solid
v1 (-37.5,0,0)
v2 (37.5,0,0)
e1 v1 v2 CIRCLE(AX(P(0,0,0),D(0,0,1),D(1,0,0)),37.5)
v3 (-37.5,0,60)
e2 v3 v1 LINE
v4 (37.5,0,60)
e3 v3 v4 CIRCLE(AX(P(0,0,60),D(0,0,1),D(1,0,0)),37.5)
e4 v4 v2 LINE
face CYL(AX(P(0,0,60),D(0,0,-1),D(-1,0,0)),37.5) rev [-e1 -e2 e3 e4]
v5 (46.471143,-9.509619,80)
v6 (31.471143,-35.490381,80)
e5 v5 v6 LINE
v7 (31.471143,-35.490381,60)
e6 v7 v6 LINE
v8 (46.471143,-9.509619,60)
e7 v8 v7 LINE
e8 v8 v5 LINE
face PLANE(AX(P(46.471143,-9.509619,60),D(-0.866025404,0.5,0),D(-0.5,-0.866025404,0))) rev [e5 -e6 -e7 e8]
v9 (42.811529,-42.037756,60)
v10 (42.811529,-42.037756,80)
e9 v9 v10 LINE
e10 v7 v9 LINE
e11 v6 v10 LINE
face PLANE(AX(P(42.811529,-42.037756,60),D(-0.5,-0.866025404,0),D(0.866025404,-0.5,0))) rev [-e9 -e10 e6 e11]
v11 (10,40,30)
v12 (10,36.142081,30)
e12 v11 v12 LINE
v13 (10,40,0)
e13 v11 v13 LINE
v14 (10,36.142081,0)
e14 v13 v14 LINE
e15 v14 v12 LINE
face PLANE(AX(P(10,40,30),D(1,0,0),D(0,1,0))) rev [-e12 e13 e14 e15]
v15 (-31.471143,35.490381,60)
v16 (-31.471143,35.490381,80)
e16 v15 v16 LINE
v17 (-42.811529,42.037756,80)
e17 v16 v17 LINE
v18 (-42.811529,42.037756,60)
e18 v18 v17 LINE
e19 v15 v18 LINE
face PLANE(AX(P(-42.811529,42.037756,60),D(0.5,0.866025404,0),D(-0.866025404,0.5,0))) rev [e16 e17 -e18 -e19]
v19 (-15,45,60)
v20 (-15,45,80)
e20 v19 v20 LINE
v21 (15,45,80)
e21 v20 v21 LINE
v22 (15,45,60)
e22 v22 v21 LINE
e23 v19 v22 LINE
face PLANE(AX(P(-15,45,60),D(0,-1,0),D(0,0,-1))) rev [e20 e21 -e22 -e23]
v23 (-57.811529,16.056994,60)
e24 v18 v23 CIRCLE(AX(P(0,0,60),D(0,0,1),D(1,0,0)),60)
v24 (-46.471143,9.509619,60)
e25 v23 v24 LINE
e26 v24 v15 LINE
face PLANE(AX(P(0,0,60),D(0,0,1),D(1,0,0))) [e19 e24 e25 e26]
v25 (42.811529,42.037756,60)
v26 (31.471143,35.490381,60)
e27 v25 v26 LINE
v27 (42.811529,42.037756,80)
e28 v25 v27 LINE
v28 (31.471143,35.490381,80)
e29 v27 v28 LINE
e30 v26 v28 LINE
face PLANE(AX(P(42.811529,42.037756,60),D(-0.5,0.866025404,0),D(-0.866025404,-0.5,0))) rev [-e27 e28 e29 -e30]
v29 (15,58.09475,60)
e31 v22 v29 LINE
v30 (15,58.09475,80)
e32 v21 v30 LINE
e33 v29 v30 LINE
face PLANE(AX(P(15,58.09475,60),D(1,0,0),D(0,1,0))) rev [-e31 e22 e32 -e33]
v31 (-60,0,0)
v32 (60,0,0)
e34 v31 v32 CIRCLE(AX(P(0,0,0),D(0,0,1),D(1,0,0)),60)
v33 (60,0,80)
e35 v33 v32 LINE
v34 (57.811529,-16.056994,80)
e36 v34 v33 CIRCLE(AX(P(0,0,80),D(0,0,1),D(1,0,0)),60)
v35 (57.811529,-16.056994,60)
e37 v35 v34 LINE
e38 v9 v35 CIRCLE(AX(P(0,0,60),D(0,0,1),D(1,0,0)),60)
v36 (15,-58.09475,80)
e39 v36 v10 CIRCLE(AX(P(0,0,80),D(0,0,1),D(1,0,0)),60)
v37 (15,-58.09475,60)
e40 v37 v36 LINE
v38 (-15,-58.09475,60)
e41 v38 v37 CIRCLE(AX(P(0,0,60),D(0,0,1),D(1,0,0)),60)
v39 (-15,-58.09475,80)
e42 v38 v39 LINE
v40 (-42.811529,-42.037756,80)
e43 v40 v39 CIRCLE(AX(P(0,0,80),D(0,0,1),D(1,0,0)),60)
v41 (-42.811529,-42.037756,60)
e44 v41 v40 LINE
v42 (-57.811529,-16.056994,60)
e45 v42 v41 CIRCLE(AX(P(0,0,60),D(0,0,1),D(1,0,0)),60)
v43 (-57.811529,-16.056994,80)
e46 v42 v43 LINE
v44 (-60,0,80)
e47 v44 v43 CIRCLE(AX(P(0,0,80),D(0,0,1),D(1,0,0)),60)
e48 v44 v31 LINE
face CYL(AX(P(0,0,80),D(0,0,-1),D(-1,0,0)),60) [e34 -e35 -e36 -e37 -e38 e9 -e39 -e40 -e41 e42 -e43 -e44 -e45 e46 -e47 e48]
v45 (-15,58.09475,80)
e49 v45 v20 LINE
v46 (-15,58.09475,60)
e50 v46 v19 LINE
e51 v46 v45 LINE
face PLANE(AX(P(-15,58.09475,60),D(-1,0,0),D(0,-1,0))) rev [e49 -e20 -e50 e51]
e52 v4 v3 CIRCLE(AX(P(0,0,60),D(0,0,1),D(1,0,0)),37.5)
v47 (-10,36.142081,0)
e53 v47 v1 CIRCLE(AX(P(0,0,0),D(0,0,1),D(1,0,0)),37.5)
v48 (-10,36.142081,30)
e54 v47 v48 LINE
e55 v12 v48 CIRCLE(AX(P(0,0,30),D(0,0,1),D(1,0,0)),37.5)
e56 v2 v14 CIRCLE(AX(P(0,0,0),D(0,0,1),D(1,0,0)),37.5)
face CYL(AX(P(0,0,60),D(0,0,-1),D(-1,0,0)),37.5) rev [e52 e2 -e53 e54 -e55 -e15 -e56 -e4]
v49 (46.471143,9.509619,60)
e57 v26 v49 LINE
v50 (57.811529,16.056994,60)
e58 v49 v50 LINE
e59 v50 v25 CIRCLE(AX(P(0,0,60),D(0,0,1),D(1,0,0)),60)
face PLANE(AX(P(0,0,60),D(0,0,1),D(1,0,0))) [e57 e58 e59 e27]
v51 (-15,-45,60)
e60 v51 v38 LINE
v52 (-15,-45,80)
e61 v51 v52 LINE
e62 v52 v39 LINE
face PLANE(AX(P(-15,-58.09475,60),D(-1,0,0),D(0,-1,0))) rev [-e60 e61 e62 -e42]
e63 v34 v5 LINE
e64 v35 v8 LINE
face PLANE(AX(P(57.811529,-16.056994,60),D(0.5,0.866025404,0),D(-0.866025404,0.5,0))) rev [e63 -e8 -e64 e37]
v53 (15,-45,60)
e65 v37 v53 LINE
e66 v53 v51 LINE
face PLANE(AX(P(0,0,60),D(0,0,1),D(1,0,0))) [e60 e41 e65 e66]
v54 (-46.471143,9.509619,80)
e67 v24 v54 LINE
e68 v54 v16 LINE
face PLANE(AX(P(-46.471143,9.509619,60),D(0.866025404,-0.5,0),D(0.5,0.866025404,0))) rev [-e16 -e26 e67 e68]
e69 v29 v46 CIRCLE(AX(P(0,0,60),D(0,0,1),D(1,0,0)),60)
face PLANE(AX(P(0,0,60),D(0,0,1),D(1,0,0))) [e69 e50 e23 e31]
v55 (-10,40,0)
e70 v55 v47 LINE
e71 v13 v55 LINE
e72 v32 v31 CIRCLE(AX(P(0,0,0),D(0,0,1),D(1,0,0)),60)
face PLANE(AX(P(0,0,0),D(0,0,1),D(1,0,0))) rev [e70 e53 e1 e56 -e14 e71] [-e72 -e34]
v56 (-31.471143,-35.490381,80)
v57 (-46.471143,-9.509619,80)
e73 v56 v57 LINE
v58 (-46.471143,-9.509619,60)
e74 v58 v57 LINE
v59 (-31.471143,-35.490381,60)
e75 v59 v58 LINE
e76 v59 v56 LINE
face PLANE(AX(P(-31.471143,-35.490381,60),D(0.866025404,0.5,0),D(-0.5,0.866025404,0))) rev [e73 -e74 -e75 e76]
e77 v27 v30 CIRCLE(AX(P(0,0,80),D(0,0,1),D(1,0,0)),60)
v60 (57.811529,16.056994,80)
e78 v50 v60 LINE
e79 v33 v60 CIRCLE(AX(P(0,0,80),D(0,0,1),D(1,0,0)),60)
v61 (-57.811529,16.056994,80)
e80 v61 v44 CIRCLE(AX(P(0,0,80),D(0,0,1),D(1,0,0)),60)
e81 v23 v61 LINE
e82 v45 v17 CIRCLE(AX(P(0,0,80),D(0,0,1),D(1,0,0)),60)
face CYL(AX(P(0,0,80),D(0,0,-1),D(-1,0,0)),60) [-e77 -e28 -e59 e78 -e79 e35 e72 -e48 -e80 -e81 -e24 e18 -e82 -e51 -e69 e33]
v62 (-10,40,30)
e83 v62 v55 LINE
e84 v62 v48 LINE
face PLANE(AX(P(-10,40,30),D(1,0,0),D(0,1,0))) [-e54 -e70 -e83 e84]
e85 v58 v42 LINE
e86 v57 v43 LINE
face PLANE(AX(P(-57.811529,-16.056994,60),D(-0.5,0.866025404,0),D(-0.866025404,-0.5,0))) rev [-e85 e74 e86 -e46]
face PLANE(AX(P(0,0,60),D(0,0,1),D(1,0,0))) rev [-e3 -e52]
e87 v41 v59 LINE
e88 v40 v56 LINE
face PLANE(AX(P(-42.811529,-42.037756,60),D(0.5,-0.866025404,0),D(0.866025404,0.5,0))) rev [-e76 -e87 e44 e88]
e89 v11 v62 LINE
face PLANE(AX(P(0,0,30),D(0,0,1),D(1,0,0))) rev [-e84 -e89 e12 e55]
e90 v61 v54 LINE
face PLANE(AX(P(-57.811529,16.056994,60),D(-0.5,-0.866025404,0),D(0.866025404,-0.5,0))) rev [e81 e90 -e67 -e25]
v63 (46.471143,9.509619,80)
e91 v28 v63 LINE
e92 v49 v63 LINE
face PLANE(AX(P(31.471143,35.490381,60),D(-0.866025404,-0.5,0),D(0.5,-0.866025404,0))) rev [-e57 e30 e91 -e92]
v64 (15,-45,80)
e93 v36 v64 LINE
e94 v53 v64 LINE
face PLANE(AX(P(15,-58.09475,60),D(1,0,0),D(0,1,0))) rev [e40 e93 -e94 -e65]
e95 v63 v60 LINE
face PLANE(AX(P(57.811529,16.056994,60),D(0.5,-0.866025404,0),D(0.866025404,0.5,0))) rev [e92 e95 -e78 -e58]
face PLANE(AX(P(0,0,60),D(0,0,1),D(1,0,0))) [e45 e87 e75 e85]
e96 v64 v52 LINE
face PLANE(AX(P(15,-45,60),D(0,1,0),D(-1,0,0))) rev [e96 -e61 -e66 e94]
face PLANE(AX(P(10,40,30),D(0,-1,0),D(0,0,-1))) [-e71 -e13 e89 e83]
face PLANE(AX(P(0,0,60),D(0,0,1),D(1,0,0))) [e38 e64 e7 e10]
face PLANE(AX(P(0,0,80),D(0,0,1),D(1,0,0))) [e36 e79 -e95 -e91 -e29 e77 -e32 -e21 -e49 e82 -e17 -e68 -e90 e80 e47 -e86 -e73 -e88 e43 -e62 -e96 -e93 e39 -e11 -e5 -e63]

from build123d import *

# Parameters (mm, degrees)
SKETCH_2_R          = 60
EXTRUDE_1_DEPTH     = 80
SKETCH_1_R          = 37.5
CUT_EXTRUDE_1_DEPTH = 60
CUT_EXTRUDE_START   = -20
CUT_EXTRUDE_2_DEPTH = 20
SKETCH_4_W          = 20
SKETCH_4_H          = 11.668393693
CUT_EXTRUDE_3_DEPTH = 30


with BuildPart() as part:
    # 草图2 → 凸台-拉伸1 (new body)
    with BuildSketch(Plane.XY):
        Circle(SKETCH_2_R)
    extrude(amount=EXTRUDE_1_DEPTH)

    # 草图1 → 切除-拉伸1 (cut)
    with BuildSketch(Plane.XY):
        Circle(SKETCH_1_R)
    extrude(amount=CUT_EXTRUDE_1_DEPTH, mode=Mode.SUBTRACT)

    # 草图3 → 切除-拉伸2 (cut)
    with BuildSketch(Plane.XY.offset(80).offset(CUT_EXTRUDE_START)):
        with BuildLine():
            Line((57.811529494, 16.05699404), (46.47114317, 9.509618943))
            Line((46.47114317, 9.509618943), (31.47114317, 35.490381057))
            Line((31.47114317, 35.490381057), (42.811529494, 42.037756153))
            ThreePointArc((42.811529494, 42.037756153), (51.961524227, 30), (57.811529494, 16.05699404))
        make_face()
        with BuildLine():
            Line((-15, 58.094750193), (-15, 45))
            Line((-15, 45), (15, 45))
            Line((15, 45), (15, 58.094750193))
            ThreePointArc((15, 58.094750193), (0, 60), (-15, 58.094750193))
        make_face()
        with BuildLine():
            Line((42.811529494, -42.037756153), (31.47114317, -35.490381057))
            Line((31.47114317, -35.490381057), (46.47114317, -9.509618943))
            Line((46.47114317, -9.509618943), (57.811529494, -16.05699404))
            ThreePointArc((57.811529494, -16.05699404), (51.961524227, -30), (42.811529494, -42.037756153))
        make_face()
        with BuildLine():
            Line((-15, -58.094750193), (-15, -45))
            Line((-15, -45), (15, -45))
            Line((15, -45), (15, -58.094750193))
            ThreePointArc((15, -58.094750193), (0, -60), (-15, -58.094750193))
        make_face()
        with BuildLine():
            Line((-57.811529494, -16.05699404), (-46.47114317, -9.509618943))
            Line((-46.47114317, -9.509618943), (-31.47114317, -35.490381057))
            Line((-31.47114317, -35.490381057), (-42.811529494, -42.037756153))
            ThreePointArc((-42.811529494, -42.037756153), (-51.961524227, -30), (-57.811529494, -16.05699404))
        make_face()
        with BuildLine():
            Line((-42.811529494, 42.037756153), (-31.47114317, 35.490381057))
            Line((-31.47114317, 35.490381057), (-46.47114317, 9.509618943))
            Line((-46.47114317, 9.509618943), (-57.811529494, 16.05699404))
            ThreePointArc((-57.811529494, 16.05699404), (-51.961524227, 30), (-42.811529494, 42.037756153))
        make_face()
    extrude(amount=CUT_EXTRUDE_2_DEPTH, mode=Mode.SUBTRACT)

    # 草图4 → 切除-拉伸3 (cut)
    with BuildSketch(Plane(origin=(0, 0, 0), x_dir=(-1, 0, 0), z_dir=(0, 0, -1))):
        with Locations((0, 34.165803154)):
            Rectangle(SKETCH_4_W, SKETCH_4_H)
    extrude(amount=-CUT_EXTRUDE_3_DEPTH, mode=Mode.SUBTRACT)


solid = part.part
